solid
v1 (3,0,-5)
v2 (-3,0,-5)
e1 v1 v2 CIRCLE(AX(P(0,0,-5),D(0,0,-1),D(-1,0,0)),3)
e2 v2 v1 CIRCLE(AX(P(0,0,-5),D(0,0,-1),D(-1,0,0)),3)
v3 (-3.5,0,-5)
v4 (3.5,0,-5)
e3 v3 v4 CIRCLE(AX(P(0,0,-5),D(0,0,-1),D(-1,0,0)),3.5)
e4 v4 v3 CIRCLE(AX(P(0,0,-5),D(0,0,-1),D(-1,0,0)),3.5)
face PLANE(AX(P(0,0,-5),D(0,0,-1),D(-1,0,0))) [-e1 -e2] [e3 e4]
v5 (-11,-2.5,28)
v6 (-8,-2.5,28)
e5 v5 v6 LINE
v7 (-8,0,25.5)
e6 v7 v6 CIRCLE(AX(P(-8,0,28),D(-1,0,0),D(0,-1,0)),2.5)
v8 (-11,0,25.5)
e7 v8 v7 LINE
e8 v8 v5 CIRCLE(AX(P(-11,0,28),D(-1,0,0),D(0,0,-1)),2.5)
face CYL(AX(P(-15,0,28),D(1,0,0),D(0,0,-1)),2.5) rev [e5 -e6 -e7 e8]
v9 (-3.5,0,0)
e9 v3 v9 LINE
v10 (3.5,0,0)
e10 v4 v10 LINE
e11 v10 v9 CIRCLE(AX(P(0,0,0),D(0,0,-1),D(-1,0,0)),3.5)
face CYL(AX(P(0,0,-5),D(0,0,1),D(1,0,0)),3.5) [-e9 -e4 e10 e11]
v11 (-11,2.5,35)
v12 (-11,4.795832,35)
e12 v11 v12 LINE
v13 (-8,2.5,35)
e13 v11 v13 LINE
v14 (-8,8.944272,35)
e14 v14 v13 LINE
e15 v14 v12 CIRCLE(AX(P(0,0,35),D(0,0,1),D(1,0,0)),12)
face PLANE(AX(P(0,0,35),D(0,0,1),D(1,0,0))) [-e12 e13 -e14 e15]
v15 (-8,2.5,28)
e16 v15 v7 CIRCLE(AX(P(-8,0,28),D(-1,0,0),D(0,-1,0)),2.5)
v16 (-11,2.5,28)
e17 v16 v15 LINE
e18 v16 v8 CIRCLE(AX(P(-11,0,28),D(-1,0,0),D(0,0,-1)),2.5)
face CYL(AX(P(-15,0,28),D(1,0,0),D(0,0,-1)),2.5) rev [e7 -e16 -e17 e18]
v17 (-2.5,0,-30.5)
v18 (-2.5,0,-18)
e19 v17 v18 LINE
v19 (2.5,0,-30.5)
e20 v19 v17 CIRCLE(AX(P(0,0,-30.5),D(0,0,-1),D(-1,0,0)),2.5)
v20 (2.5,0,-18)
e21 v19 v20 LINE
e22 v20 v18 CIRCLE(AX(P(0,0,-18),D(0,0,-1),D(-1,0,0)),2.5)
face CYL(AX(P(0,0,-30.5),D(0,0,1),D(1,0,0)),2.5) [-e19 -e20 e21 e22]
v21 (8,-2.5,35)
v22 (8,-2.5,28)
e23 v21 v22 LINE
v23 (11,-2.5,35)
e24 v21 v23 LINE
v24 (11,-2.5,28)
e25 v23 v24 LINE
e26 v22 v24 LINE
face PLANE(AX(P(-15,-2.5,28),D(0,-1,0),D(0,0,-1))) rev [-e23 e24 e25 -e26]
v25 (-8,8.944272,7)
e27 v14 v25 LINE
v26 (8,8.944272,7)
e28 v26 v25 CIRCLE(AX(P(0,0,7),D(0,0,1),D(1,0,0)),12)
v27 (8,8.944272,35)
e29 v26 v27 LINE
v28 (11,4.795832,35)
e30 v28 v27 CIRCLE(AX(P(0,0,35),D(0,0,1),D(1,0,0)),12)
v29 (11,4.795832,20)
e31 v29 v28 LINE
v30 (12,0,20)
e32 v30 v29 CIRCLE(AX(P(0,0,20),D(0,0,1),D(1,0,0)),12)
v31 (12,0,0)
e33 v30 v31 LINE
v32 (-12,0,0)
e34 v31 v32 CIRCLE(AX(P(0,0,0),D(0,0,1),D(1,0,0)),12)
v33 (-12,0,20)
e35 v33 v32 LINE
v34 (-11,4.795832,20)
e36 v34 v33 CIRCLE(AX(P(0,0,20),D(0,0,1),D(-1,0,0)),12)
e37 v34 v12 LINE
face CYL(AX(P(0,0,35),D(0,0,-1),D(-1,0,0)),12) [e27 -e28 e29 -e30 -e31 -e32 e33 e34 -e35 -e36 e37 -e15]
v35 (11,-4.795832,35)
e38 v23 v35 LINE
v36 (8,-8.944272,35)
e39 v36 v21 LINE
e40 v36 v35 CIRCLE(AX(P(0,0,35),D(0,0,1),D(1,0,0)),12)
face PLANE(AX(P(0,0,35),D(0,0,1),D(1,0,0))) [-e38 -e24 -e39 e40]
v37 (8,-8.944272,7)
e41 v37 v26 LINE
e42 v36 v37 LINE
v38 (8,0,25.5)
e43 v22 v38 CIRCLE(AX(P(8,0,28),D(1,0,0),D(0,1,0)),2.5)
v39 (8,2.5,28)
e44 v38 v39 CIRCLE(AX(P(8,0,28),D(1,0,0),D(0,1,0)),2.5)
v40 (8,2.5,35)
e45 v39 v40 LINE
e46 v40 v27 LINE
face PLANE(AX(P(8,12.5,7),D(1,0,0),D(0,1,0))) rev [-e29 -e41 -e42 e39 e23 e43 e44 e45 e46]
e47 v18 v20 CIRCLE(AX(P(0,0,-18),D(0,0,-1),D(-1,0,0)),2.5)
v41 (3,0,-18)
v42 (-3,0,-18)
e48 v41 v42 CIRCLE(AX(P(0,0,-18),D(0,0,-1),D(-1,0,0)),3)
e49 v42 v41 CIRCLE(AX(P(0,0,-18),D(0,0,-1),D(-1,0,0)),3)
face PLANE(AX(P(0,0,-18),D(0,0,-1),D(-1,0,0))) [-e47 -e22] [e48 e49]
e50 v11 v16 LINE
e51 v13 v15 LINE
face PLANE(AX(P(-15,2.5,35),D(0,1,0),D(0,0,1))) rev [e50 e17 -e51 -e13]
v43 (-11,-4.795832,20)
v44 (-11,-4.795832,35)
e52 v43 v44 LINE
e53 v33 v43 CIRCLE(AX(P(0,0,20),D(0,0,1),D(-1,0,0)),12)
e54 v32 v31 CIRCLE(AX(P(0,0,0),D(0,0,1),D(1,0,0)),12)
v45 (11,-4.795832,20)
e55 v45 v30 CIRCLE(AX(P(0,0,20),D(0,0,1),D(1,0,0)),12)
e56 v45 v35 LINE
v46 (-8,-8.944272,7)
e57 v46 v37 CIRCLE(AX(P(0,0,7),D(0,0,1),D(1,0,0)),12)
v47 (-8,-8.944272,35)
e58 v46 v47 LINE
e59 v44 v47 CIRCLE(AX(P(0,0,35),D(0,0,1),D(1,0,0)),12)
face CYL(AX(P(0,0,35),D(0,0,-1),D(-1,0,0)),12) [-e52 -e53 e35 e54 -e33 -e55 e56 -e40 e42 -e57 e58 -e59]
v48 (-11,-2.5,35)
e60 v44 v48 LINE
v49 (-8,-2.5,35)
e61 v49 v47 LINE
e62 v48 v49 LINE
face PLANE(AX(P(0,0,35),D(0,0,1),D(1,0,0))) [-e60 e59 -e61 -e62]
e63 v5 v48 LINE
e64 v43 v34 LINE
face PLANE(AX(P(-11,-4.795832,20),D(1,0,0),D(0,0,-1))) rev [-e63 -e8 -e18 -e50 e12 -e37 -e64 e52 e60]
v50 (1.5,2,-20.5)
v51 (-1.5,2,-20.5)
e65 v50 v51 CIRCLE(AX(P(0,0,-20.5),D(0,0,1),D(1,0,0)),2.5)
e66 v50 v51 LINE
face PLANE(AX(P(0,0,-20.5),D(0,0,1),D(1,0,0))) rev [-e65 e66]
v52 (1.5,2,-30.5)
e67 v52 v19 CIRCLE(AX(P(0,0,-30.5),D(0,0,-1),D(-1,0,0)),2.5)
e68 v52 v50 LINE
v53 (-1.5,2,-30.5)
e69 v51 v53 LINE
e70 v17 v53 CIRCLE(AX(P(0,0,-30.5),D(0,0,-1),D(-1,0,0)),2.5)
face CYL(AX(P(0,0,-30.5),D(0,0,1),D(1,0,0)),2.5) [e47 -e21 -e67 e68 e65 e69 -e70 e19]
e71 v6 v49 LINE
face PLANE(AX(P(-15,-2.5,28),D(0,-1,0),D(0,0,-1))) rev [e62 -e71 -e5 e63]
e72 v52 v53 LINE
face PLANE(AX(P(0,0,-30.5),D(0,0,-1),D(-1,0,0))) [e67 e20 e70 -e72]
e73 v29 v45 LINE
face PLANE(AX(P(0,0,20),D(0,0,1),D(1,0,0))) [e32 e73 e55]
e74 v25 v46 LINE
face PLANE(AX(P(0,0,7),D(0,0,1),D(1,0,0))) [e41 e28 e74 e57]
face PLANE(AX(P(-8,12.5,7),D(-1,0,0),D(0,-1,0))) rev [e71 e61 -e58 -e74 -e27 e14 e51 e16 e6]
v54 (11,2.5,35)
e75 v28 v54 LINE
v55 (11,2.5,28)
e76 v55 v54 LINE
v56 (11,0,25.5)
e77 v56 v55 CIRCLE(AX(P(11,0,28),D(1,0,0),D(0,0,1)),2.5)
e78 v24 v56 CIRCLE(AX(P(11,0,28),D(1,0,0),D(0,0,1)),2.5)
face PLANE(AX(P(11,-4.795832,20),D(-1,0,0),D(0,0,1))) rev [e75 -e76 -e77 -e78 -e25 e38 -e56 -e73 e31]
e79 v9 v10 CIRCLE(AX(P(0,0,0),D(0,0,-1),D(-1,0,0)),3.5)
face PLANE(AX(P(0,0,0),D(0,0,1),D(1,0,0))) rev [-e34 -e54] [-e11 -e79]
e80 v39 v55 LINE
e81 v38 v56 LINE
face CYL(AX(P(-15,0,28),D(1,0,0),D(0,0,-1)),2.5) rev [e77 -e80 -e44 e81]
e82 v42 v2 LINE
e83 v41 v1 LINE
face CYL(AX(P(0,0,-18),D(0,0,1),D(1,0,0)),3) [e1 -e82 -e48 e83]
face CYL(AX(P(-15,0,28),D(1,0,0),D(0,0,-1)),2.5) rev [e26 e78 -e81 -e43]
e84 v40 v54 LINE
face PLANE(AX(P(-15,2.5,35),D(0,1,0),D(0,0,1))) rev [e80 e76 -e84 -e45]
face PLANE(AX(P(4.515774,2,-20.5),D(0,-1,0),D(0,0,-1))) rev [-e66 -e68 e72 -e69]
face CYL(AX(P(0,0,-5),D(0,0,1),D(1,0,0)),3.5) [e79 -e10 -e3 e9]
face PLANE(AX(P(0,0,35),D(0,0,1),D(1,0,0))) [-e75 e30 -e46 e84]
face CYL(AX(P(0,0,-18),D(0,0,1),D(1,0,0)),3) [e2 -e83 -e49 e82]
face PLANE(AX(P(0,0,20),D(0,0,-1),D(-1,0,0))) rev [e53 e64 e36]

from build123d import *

# Parameters (mm, degrees)
SKETCH1_R           = 12
BOSS_EXTRUDE1_DEPTH = 35
SKETCH2_R           = 3.5
BOSS_EXTRUDE2_DEPTH = 5
SKETCH3_W           = 16
SKETCH3_H           = 25
CUT_EXTRUDE1_DEPTH  = 28
CUT_EXTRUDE2_DEPTH  = 15
CUT_EXTRUDE3_START  = -15
CUT_EXTRUDE3_DEPTH  = 15
SKETCH6_R           = 3
BOSS_EXTRUDE3_DEPTH = 13
SKETCH7_R           = 2.5
BOSS_EXTRUDE4_DEPTH = 12.5
SKETCH8_W           = 9.031547502
SKETCH8_H           = 2.523978301
CUT_EXTRUDE4_DEPTH  = 10


with BuildPart() as part:
    # Sketch1 → Boss-Extrude1 (new body)
    with BuildSketch(Plane.XY):
        Circle(SKETCH1_R)
    extrude(amount=BOSS_EXTRUDE1_DEPTH)

    # Sketch2 → Boss-Extrude2 (add)
    with BuildSketch(Plane(origin=(0, 0, 0), x_dir=(-1, 0, 0), z_dir=(0, 0, -1))):
        Circle(SKETCH2_R)
    extrude(amount=BOSS_EXTRUDE2_DEPTH)

    # Sketch3 → Cut-Extrude1 (cut)
    with BuildSketch(Plane.XY.offset(35)):
        Rectangle(SKETCH3_W, SKETCH3_H)
    extrude(amount=-CUT_EXTRUDE1_DEPTH, mode=Mode.SUBTRACT)

    # Sketch4 → Cut-Extrude2 (cut, symmetric)
    with BuildSketch(Plane(origin=(0, 0, 0), x_dir=(0, 0, -1), z_dir=(1, 0, 0))):
        with BuildLine():
            Line((-28, -2.5), (-35, -2.5))
            Line((-35, -2.5), (-35, 2.5))
            Line((-35, 2.5), (-28, 2.5))
            ThreePointArc((-28, 2.5), (-25.5, 0), (-28, -2.5))
        make_face()
    extrude(amount=CUT_EXTRUDE2_DEPTH, both=True, mode=Mode.SUBTRACT)

    # Sketch5 → Cut-Extrude3 (cut)
    with BuildSketch(Plane.XY.offset(35).offset(CUT_EXTRUDE3_START)):
        with BuildLine():
            Line((11, -4.795831523), (11, 4.795831523))
            ThreePointArc((11, 4.795831523), (12, 0), (11, -4.795831523))
        make_face()
        with BuildLine():
            Line((-11, -4.795831523), (-11, 4.795831523))
            ThreePointArc((-11, 4.795831523), (-12, 0), (-11, -4.795831523))
        make_face()
    extrude(amount=CUT_EXTRUDE3_DEPTH, mode=Mode.SUBTRACT)

    # Sketch6 → Boss-Extrude3 (add)
    with BuildSketch(Plane(origin=(0, 0, -5), x_dir=(-1, 0, 0), z_dir=(0, 0, -1))):
        with Locations(Location((0, 0, 0), (0, 0, 180))):
            Circle(SKETCH6_R)
    extrude(amount=BOSS_EXTRUDE3_DEPTH)

    # Sketch7 → Boss-Extrude4 (add)
    with BuildSketch(Plane(origin=(0, 0, -18), x_dir=(-1, 0, 0), z_dir=(0, 0, -1))):
        Circle(SKETCH7_R)
    extrude(amount=BOSS_EXTRUDE4_DEPTH)

    # Sketch8 → Cut-Extrude4 (cut)
    with BuildSketch(Plane(origin=(0, 0, -30.5), x_dir=(-1, 0, 0), z_dir=(0, 0, -1))):
        with Locations((0, 3.261989151)):
            Rectangle(SKETCH8_W, SKETCH8_H)
    extrude(amount=-CUT_EXTRUDE4_DEPTH, mode=Mode.SUBTRACT)


solid = part.part
